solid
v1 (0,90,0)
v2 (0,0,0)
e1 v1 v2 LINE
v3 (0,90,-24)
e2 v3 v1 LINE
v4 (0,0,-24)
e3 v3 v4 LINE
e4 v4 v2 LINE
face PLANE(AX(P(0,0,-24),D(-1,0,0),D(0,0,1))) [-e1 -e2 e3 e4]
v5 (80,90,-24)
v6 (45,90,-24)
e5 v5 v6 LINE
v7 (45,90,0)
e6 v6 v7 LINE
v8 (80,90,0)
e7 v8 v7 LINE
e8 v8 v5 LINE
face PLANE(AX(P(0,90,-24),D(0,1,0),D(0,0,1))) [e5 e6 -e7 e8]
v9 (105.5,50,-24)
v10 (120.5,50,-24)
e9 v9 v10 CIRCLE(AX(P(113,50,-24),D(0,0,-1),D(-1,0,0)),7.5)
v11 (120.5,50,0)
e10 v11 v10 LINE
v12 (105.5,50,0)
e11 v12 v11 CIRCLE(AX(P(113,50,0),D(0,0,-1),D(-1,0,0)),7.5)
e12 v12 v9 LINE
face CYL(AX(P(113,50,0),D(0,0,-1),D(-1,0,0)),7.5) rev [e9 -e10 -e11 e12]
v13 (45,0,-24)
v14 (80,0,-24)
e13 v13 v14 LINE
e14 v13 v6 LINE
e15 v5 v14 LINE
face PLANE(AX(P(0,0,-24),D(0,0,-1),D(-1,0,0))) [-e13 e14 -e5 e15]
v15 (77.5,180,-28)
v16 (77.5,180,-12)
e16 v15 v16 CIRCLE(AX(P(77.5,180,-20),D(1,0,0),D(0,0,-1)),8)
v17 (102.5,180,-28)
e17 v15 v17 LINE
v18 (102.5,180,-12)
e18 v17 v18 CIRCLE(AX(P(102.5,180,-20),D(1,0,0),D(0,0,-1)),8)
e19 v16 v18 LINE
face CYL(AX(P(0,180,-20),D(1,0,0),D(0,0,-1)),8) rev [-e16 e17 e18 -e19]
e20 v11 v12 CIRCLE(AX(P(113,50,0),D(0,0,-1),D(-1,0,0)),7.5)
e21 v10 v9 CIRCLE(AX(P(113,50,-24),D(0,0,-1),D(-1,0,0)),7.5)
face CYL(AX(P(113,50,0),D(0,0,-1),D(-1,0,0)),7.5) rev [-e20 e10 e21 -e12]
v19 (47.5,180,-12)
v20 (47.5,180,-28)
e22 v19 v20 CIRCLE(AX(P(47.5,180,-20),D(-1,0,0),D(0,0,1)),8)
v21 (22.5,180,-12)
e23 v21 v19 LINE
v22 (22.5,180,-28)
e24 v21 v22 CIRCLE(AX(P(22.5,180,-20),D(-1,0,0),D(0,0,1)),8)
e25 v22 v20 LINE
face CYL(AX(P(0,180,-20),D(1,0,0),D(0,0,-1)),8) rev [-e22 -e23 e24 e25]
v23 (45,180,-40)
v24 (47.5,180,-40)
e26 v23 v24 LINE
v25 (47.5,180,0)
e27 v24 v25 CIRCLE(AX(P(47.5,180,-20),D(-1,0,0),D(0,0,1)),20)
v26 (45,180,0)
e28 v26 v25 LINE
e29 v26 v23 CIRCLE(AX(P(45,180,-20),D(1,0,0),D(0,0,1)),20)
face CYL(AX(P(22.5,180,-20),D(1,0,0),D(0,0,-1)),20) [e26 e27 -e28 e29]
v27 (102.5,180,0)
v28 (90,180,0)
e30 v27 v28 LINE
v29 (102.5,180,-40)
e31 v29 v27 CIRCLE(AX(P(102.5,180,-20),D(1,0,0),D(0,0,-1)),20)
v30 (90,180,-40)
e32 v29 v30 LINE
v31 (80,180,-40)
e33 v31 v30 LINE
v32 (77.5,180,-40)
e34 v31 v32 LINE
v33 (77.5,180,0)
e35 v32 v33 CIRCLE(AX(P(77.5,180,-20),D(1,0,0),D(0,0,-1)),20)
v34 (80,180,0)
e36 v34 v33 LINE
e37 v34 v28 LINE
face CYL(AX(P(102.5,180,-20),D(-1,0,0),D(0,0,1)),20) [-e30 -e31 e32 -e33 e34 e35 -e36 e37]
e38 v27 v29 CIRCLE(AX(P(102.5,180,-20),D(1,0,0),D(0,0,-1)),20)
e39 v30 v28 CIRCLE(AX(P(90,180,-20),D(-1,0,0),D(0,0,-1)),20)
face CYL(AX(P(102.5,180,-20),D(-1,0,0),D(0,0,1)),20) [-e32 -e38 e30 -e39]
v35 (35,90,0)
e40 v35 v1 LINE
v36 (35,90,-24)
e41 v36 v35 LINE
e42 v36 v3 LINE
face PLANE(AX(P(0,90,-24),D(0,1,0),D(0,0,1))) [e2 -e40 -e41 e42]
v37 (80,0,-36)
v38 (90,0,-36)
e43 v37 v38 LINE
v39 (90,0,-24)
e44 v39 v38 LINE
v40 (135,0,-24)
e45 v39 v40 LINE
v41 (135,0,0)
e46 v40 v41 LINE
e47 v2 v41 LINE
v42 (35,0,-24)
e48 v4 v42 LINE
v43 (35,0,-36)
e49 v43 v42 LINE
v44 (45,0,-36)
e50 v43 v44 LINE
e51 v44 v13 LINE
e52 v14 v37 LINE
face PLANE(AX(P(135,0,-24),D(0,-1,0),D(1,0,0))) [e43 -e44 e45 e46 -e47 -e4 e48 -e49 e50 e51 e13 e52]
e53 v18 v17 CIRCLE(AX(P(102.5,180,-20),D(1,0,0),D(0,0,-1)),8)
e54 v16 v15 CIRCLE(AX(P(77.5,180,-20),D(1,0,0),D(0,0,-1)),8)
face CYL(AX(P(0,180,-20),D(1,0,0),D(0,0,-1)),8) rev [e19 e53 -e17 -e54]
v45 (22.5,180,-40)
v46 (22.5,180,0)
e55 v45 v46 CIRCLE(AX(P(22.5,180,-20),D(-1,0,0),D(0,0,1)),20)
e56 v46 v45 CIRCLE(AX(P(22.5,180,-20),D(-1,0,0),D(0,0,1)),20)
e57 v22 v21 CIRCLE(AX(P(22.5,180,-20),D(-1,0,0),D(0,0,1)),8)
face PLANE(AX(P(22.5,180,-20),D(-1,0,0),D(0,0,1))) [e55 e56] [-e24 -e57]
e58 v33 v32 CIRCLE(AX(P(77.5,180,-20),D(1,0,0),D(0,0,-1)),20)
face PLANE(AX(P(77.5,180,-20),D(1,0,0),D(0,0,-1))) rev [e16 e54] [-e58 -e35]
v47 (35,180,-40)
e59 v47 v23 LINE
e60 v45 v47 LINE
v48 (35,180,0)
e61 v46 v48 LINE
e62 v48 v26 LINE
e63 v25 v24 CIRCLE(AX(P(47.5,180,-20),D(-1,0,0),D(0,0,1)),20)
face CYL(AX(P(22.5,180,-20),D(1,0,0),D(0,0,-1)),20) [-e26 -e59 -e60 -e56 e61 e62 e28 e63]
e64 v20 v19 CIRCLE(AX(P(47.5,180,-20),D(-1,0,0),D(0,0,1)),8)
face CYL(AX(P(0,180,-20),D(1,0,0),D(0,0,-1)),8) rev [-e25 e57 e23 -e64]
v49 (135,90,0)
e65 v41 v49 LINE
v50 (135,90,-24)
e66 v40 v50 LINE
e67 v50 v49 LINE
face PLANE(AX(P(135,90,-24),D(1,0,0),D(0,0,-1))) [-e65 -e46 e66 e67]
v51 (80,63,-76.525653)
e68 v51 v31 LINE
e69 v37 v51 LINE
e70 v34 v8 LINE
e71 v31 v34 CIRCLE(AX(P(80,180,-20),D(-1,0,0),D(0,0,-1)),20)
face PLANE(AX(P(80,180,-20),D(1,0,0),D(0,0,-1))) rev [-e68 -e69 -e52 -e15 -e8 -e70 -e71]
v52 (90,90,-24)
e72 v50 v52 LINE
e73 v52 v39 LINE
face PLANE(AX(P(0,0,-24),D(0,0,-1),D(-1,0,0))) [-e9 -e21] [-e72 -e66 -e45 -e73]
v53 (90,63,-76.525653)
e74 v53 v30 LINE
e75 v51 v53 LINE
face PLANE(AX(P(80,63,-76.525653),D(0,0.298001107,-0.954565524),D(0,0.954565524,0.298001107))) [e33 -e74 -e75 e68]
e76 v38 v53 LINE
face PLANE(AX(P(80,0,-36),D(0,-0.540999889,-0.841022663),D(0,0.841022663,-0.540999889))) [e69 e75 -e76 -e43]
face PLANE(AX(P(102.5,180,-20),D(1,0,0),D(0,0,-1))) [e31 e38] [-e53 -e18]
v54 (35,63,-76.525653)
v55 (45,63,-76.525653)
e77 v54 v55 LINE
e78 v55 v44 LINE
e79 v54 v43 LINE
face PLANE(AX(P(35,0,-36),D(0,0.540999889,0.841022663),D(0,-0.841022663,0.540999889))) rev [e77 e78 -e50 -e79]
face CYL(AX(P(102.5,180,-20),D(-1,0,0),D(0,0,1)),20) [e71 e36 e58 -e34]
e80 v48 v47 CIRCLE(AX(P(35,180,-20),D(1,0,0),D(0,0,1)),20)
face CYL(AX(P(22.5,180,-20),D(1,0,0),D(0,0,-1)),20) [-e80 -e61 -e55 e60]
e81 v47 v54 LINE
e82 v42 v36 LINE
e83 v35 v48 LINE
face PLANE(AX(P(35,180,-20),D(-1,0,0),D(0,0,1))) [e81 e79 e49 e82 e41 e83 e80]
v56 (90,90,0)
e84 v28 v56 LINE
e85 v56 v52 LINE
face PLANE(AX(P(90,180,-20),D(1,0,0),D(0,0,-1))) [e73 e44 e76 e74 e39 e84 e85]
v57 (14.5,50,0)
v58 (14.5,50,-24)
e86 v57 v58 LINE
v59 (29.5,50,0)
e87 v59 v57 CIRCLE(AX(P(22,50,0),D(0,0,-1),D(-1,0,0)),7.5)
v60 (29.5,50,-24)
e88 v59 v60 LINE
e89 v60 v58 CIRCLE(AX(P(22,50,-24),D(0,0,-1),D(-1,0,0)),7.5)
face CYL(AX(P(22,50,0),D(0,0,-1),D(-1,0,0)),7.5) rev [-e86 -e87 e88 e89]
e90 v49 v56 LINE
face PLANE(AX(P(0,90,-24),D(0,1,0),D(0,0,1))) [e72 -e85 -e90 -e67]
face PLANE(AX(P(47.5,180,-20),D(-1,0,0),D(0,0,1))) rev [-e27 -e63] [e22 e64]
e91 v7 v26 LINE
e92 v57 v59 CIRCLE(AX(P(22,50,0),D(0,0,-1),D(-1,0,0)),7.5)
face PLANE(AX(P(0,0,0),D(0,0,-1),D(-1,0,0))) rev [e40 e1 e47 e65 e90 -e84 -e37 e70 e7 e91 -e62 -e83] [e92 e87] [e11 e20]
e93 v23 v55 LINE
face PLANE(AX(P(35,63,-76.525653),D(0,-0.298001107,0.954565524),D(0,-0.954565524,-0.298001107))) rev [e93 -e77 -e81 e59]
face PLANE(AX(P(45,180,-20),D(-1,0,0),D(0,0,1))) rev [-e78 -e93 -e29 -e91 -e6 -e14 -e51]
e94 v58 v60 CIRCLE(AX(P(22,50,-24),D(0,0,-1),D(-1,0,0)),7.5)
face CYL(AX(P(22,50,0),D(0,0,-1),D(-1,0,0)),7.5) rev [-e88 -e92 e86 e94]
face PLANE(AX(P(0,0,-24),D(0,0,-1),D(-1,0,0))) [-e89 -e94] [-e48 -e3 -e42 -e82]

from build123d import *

# Parameters (mm, degrees)
BASE_PLATE_SKETCH_W     = 135
BASE_PLATE_SKETCH_H     = 90
BASE_PLATE_DEPTH        = 24
LUG_1_DEPTH             = 10
LUG_1_BOSS_SKETCH_R     = 20
LUG_1_PIVOT_BOSS_DEPTH  = 12.5
LUG_2_DEPTH             = 10
LUG_2_BOSS_SKETCH_R     = 20
LUG_2_PIVOT_BOSS_DEPTH  = 12.5
PIVOT_HOLE_SKETCH_R     = 8
PIVOT_HOLE_16_DEPTH     = 238.407720253
MOUNTING_HOLES_SKETCH_R = 7.5
MOUNTING_HOLES_2X_DEPTH = 247.94927469


with BuildPart() as part:
    # Base Plate Sketch → Base Plate (new body)
    with BuildSketch(Plane.XY):
        with Locations((67.5, 45)):
            Rectangle(BASE_PLATE_SKETCH_W, BASE_PLATE_SKETCH_H)
    extrude(amount=-BASE_PLATE_DEPTH)

    # Lug 1 Profile → Lug 1 (add)
    with BuildSketch(Plane(origin=(90, 0, 0), x_dir=(0, 0, -1), z_dir=(1, 0, 0))):
        with BuildLine():
            Line((0, 90), (0, 180))
            ThreePointArc((0, 180), (20, 160), (40, 180))
            Line((40, 180), (76.525653448, 63))
            Line((76.525653448, 63), (36, 0))
            Line((36, 0), (24, 0))
            Line((24, 0), (24, 90))
            Line((24, 90), (0, 90))
        make_face()
    extrude(amount=-LUG_1_DEPTH)

    # Lug 1 Boss Sketch → Lug 1 Pivot Boss (add, symmetric)
    with BuildSketch(Plane(origin=(90, 0, 0), x_dir=(0, 0, -1), z_dir=(1, 0, 0))):
        with Locations((20, 180)):
            Circle(LUG_1_BOSS_SKETCH_R)
    extrude(amount=LUG_1_PIVOT_BOSS_DEPTH, both=True)

    # Lug 2 Profile → Lug 2 (add)
    with BuildSketch(Plane.ZY.offset(-45)):
        with BuildLine():
            Line((-24, 0), (-36, 0))
            Line((-36, 0), (-76.525653448, 63))
            Line((-76.525653448, 63), (-40, 180))
            ThreePointArc((-40, 180), (-20, 160), (0, 180))
            Line((0, 180), (0, 90))
            Line((0, 90), (-24, 90))
            Line((-24, 90), (-24, 0))
        make_face()
    extrude(amount=LUG_2_DEPTH)

    # Lug 2 Boss Sketch → Lug 2 Pivot Boss (add, symmetric)
    with BuildSketch(Plane.ZY.offset(-35)):
        with Locations(Location((-20, 180, 0), (0, 0, 180))):
            Circle(LUG_2_BOSS_SKETCH_R)
    extrude(amount=LUG_2_PIVOT_BOSS_DEPTH, both=True)

    # Pivot Hole Sketch → Pivot Hole Ø16 (cut, through all)
    with BuildSketch(Plane(origin=(102.5, 0, 0), x_dir=(0, 0, -1), z_dir=(1, 0, 0))):
        with Locations(Location((20, 180, 0), (0, 0, 180))):
            Circle(PIVOT_HOLE_SKETCH_R)
    extrude(amount=-PIVOT_HOLE_16_DEPTH, mode=Mode.SUBTRACT)

    # Mounting Holes Sketch → Mounting Holes 2x (cut, through all)
    with BuildSketch(Plane(origin=(0, 0, -24), x_dir=(-1, 0, 0), z_dir=(0, 0, -1))):
        with Locations((-113, 50)):
            Circle(MOUNTING_HOLES_SKETCH_R)
        with Locations((-22, 50)):
            Circle(MOUNTING_HOLES_SKETCH_R)
    extrude(amount=-MOUNTING_HOLES_2X_DEPTH, mode=Mode.SUBTRACT)


solid = part.part
